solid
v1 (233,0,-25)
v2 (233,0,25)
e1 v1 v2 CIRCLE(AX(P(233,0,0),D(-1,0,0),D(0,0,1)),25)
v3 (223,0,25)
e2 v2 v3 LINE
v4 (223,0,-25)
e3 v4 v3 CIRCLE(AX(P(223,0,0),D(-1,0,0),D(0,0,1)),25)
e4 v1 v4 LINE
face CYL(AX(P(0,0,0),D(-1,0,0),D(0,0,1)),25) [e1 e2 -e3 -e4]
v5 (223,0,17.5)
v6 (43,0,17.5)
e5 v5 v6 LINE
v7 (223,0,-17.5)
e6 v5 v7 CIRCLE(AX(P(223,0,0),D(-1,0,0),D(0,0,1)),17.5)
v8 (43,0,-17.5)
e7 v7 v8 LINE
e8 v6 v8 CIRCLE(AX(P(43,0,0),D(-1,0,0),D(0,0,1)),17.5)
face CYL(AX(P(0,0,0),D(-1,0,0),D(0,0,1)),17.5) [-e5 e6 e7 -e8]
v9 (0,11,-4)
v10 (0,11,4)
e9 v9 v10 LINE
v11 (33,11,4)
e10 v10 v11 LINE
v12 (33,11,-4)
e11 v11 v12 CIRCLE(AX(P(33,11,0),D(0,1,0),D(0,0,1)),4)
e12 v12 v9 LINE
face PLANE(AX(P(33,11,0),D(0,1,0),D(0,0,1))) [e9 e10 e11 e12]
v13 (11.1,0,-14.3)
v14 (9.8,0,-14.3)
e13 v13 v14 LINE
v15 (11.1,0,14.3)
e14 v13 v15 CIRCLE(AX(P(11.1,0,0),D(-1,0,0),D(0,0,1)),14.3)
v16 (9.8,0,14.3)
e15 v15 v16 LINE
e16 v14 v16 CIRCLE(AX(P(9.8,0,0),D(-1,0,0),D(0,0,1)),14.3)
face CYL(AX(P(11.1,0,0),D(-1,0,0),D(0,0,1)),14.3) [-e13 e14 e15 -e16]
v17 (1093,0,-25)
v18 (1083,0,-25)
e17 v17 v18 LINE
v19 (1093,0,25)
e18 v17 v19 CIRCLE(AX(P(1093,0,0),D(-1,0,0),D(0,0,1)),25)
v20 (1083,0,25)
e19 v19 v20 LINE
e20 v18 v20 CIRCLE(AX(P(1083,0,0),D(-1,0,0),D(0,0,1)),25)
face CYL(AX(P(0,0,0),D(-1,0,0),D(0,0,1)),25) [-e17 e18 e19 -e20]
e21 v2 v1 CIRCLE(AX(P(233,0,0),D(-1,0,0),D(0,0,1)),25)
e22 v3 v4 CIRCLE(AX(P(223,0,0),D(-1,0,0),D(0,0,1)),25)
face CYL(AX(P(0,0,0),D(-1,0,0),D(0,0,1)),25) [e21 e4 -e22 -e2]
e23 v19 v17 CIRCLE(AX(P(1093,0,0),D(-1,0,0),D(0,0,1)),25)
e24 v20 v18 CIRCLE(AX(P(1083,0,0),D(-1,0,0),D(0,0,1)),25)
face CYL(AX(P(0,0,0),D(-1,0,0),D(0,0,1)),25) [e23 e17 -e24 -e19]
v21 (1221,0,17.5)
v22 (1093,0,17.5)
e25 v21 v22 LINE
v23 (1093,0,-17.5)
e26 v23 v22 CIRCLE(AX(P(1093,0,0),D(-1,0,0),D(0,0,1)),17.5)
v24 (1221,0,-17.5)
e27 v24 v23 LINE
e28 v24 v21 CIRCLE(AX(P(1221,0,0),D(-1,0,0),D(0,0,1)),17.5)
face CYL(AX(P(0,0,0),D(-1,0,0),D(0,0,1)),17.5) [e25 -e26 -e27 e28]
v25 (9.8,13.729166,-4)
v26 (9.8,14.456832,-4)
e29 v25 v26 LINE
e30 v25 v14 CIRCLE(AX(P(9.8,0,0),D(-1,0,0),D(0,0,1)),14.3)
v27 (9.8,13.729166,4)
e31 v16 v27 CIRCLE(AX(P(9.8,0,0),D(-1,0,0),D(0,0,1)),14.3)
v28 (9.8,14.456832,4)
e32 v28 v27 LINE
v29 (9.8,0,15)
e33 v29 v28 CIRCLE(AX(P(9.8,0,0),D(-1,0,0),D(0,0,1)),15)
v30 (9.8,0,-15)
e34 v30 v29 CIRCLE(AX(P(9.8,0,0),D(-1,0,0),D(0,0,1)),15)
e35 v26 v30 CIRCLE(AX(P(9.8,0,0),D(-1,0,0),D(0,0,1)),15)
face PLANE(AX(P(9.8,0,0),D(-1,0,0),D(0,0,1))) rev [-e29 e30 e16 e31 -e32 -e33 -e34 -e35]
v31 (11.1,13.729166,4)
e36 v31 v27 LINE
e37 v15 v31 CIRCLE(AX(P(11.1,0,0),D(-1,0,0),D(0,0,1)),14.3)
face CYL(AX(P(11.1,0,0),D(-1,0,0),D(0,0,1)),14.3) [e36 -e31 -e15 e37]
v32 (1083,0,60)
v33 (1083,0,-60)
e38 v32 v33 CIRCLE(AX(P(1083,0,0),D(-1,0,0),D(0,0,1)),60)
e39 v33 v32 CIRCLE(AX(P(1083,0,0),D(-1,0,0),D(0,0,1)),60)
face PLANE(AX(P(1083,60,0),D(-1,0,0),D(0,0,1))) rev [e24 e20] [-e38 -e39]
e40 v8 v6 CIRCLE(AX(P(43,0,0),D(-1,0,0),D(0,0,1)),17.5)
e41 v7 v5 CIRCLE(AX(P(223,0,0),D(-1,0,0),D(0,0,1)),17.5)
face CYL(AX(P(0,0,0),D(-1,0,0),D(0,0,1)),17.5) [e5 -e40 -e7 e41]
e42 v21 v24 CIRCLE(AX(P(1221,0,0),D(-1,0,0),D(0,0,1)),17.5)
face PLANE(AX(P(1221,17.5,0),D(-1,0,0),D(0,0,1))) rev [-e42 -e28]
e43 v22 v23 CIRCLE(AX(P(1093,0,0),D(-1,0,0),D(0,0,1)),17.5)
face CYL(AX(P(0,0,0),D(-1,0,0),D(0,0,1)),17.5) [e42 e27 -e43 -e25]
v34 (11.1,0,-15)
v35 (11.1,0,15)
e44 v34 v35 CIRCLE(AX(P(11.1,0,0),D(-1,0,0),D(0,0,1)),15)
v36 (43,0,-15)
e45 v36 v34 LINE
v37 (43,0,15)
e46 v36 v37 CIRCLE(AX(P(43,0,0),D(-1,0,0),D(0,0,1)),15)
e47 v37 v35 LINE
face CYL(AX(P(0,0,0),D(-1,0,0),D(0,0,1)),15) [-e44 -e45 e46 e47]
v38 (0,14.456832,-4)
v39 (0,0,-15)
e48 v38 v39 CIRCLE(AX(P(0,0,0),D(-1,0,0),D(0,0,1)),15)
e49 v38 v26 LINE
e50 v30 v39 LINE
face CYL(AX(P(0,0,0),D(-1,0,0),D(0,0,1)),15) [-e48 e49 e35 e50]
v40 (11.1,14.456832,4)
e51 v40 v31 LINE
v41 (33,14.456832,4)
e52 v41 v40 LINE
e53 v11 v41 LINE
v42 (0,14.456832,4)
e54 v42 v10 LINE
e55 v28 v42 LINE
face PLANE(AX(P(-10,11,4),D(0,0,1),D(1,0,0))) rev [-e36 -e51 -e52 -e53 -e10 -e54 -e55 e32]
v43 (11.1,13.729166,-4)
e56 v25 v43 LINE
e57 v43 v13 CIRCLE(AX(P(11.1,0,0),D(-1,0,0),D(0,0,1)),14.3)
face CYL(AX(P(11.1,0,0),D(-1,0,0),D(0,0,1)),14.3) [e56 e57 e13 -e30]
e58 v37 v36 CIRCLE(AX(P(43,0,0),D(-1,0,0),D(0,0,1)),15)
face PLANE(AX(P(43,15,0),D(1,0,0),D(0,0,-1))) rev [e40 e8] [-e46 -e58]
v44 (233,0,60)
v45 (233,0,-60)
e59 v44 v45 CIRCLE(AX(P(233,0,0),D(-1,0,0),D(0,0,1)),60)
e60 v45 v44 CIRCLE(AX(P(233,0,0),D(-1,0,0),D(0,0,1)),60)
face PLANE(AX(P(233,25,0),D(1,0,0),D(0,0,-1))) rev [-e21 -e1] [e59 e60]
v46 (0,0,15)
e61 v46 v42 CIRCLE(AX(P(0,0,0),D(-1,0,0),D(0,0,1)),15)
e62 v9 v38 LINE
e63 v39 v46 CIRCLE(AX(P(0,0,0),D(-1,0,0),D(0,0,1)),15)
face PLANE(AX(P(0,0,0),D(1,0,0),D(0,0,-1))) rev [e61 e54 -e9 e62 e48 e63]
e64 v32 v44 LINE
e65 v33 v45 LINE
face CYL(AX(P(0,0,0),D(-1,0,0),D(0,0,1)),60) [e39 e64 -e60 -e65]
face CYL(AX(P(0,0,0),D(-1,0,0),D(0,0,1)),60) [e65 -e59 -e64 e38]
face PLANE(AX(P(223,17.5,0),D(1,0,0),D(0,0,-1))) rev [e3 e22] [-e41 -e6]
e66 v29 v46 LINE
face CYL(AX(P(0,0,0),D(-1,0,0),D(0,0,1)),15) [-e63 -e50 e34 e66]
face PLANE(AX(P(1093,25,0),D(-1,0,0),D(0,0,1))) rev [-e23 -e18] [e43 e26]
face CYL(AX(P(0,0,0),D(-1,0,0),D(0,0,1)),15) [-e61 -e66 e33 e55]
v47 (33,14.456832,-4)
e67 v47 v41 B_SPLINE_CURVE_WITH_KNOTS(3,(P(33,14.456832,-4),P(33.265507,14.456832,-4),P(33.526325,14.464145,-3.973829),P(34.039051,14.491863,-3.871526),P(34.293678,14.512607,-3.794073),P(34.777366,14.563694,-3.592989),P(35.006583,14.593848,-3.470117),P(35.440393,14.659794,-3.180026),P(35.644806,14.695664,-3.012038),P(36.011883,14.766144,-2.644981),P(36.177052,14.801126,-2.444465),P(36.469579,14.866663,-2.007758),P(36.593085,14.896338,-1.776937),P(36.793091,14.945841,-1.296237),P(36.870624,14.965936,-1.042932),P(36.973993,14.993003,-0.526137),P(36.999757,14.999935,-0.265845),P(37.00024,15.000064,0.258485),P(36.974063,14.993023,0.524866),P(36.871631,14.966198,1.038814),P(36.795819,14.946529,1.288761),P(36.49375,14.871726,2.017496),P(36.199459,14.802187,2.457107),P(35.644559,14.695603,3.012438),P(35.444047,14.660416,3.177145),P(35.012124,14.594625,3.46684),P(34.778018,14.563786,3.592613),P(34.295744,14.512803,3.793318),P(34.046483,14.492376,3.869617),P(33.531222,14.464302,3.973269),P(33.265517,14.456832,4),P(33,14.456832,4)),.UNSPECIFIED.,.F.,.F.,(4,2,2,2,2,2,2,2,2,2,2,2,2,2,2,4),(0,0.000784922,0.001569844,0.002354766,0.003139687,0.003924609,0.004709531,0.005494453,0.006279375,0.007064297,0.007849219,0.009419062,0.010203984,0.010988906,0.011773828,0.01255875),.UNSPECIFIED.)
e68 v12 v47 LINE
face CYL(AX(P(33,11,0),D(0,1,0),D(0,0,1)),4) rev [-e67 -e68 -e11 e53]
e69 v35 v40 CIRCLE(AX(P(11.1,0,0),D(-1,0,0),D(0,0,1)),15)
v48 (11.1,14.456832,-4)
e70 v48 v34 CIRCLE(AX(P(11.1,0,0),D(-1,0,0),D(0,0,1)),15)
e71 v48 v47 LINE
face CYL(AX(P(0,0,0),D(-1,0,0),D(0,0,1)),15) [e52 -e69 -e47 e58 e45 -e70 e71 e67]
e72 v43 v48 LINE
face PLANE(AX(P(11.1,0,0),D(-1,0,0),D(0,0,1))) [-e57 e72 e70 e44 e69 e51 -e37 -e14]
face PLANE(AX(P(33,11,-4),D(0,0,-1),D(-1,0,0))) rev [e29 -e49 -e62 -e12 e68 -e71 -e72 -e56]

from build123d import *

# Parameters (mm, degrees)
CUT_EXTRUDE_1_DEPTH = 4
CUT_EXTRUDE_START   = -1.3
SKETCH_3_R          = 15
SKETCH_3_R_2        = 14.3
CUT_EXTRUDE_2_DEPTH = 1.3


with BuildPart() as part:
    # 草图1 → 旋转1 (revolve)
    with BuildSketch(Plane.XY, mode=Mode.PRIVATE) as revolve_1_sk:
        Polygon((0, 0), (0, 15), (43, 15), (43, 17.5), (223, 17.5), (223, 25), (233, 25), (233, 60), (1083, 60), (1083, 25), (1093, 25), (1093, 17.5), (1221, 17.5), (1221, 0), align=None)
    revolve(revolve_1_sk.sketch.rotate(Axis((0, 0, 0), (1, 0, 0)), 90), axis=Axis((0, 0, 0), (1, 0, 0)))

    # 草图2 → 切除-拉伸1 (cut)
    with BuildSketch(Plane(origin=(0, 15, 0), x_dir=(1, 0, 0), z_dir=(0, 1, 0))):
        with BuildLine():
            Line((33, 4), (-10, 4))
            Line((-10, 4), (-10, -4))
            Line((-10, -4), (33, -4))
            ThreePointArc((33, -4), (37, 0), (33, 4))
        make_face()
    extrude(amount=-CUT_EXTRUDE_1_DEPTH, mode=Mode.SUBTRACT)

    # 草图3 → 切除-拉伸2 (cut)
    with BuildSketch(Plane.ZY.offset(-9.8).offset(CUT_EXTRUDE_START)):
        Circle(SKETCH_3_R)
        Circle(SKETCH_3_R_2, mode=Mode.SUBTRACT)
    extrude(amount=CUT_EXTRUDE_2_DEPTH, mode=Mode.SUBTRACT)


solid = part.part
